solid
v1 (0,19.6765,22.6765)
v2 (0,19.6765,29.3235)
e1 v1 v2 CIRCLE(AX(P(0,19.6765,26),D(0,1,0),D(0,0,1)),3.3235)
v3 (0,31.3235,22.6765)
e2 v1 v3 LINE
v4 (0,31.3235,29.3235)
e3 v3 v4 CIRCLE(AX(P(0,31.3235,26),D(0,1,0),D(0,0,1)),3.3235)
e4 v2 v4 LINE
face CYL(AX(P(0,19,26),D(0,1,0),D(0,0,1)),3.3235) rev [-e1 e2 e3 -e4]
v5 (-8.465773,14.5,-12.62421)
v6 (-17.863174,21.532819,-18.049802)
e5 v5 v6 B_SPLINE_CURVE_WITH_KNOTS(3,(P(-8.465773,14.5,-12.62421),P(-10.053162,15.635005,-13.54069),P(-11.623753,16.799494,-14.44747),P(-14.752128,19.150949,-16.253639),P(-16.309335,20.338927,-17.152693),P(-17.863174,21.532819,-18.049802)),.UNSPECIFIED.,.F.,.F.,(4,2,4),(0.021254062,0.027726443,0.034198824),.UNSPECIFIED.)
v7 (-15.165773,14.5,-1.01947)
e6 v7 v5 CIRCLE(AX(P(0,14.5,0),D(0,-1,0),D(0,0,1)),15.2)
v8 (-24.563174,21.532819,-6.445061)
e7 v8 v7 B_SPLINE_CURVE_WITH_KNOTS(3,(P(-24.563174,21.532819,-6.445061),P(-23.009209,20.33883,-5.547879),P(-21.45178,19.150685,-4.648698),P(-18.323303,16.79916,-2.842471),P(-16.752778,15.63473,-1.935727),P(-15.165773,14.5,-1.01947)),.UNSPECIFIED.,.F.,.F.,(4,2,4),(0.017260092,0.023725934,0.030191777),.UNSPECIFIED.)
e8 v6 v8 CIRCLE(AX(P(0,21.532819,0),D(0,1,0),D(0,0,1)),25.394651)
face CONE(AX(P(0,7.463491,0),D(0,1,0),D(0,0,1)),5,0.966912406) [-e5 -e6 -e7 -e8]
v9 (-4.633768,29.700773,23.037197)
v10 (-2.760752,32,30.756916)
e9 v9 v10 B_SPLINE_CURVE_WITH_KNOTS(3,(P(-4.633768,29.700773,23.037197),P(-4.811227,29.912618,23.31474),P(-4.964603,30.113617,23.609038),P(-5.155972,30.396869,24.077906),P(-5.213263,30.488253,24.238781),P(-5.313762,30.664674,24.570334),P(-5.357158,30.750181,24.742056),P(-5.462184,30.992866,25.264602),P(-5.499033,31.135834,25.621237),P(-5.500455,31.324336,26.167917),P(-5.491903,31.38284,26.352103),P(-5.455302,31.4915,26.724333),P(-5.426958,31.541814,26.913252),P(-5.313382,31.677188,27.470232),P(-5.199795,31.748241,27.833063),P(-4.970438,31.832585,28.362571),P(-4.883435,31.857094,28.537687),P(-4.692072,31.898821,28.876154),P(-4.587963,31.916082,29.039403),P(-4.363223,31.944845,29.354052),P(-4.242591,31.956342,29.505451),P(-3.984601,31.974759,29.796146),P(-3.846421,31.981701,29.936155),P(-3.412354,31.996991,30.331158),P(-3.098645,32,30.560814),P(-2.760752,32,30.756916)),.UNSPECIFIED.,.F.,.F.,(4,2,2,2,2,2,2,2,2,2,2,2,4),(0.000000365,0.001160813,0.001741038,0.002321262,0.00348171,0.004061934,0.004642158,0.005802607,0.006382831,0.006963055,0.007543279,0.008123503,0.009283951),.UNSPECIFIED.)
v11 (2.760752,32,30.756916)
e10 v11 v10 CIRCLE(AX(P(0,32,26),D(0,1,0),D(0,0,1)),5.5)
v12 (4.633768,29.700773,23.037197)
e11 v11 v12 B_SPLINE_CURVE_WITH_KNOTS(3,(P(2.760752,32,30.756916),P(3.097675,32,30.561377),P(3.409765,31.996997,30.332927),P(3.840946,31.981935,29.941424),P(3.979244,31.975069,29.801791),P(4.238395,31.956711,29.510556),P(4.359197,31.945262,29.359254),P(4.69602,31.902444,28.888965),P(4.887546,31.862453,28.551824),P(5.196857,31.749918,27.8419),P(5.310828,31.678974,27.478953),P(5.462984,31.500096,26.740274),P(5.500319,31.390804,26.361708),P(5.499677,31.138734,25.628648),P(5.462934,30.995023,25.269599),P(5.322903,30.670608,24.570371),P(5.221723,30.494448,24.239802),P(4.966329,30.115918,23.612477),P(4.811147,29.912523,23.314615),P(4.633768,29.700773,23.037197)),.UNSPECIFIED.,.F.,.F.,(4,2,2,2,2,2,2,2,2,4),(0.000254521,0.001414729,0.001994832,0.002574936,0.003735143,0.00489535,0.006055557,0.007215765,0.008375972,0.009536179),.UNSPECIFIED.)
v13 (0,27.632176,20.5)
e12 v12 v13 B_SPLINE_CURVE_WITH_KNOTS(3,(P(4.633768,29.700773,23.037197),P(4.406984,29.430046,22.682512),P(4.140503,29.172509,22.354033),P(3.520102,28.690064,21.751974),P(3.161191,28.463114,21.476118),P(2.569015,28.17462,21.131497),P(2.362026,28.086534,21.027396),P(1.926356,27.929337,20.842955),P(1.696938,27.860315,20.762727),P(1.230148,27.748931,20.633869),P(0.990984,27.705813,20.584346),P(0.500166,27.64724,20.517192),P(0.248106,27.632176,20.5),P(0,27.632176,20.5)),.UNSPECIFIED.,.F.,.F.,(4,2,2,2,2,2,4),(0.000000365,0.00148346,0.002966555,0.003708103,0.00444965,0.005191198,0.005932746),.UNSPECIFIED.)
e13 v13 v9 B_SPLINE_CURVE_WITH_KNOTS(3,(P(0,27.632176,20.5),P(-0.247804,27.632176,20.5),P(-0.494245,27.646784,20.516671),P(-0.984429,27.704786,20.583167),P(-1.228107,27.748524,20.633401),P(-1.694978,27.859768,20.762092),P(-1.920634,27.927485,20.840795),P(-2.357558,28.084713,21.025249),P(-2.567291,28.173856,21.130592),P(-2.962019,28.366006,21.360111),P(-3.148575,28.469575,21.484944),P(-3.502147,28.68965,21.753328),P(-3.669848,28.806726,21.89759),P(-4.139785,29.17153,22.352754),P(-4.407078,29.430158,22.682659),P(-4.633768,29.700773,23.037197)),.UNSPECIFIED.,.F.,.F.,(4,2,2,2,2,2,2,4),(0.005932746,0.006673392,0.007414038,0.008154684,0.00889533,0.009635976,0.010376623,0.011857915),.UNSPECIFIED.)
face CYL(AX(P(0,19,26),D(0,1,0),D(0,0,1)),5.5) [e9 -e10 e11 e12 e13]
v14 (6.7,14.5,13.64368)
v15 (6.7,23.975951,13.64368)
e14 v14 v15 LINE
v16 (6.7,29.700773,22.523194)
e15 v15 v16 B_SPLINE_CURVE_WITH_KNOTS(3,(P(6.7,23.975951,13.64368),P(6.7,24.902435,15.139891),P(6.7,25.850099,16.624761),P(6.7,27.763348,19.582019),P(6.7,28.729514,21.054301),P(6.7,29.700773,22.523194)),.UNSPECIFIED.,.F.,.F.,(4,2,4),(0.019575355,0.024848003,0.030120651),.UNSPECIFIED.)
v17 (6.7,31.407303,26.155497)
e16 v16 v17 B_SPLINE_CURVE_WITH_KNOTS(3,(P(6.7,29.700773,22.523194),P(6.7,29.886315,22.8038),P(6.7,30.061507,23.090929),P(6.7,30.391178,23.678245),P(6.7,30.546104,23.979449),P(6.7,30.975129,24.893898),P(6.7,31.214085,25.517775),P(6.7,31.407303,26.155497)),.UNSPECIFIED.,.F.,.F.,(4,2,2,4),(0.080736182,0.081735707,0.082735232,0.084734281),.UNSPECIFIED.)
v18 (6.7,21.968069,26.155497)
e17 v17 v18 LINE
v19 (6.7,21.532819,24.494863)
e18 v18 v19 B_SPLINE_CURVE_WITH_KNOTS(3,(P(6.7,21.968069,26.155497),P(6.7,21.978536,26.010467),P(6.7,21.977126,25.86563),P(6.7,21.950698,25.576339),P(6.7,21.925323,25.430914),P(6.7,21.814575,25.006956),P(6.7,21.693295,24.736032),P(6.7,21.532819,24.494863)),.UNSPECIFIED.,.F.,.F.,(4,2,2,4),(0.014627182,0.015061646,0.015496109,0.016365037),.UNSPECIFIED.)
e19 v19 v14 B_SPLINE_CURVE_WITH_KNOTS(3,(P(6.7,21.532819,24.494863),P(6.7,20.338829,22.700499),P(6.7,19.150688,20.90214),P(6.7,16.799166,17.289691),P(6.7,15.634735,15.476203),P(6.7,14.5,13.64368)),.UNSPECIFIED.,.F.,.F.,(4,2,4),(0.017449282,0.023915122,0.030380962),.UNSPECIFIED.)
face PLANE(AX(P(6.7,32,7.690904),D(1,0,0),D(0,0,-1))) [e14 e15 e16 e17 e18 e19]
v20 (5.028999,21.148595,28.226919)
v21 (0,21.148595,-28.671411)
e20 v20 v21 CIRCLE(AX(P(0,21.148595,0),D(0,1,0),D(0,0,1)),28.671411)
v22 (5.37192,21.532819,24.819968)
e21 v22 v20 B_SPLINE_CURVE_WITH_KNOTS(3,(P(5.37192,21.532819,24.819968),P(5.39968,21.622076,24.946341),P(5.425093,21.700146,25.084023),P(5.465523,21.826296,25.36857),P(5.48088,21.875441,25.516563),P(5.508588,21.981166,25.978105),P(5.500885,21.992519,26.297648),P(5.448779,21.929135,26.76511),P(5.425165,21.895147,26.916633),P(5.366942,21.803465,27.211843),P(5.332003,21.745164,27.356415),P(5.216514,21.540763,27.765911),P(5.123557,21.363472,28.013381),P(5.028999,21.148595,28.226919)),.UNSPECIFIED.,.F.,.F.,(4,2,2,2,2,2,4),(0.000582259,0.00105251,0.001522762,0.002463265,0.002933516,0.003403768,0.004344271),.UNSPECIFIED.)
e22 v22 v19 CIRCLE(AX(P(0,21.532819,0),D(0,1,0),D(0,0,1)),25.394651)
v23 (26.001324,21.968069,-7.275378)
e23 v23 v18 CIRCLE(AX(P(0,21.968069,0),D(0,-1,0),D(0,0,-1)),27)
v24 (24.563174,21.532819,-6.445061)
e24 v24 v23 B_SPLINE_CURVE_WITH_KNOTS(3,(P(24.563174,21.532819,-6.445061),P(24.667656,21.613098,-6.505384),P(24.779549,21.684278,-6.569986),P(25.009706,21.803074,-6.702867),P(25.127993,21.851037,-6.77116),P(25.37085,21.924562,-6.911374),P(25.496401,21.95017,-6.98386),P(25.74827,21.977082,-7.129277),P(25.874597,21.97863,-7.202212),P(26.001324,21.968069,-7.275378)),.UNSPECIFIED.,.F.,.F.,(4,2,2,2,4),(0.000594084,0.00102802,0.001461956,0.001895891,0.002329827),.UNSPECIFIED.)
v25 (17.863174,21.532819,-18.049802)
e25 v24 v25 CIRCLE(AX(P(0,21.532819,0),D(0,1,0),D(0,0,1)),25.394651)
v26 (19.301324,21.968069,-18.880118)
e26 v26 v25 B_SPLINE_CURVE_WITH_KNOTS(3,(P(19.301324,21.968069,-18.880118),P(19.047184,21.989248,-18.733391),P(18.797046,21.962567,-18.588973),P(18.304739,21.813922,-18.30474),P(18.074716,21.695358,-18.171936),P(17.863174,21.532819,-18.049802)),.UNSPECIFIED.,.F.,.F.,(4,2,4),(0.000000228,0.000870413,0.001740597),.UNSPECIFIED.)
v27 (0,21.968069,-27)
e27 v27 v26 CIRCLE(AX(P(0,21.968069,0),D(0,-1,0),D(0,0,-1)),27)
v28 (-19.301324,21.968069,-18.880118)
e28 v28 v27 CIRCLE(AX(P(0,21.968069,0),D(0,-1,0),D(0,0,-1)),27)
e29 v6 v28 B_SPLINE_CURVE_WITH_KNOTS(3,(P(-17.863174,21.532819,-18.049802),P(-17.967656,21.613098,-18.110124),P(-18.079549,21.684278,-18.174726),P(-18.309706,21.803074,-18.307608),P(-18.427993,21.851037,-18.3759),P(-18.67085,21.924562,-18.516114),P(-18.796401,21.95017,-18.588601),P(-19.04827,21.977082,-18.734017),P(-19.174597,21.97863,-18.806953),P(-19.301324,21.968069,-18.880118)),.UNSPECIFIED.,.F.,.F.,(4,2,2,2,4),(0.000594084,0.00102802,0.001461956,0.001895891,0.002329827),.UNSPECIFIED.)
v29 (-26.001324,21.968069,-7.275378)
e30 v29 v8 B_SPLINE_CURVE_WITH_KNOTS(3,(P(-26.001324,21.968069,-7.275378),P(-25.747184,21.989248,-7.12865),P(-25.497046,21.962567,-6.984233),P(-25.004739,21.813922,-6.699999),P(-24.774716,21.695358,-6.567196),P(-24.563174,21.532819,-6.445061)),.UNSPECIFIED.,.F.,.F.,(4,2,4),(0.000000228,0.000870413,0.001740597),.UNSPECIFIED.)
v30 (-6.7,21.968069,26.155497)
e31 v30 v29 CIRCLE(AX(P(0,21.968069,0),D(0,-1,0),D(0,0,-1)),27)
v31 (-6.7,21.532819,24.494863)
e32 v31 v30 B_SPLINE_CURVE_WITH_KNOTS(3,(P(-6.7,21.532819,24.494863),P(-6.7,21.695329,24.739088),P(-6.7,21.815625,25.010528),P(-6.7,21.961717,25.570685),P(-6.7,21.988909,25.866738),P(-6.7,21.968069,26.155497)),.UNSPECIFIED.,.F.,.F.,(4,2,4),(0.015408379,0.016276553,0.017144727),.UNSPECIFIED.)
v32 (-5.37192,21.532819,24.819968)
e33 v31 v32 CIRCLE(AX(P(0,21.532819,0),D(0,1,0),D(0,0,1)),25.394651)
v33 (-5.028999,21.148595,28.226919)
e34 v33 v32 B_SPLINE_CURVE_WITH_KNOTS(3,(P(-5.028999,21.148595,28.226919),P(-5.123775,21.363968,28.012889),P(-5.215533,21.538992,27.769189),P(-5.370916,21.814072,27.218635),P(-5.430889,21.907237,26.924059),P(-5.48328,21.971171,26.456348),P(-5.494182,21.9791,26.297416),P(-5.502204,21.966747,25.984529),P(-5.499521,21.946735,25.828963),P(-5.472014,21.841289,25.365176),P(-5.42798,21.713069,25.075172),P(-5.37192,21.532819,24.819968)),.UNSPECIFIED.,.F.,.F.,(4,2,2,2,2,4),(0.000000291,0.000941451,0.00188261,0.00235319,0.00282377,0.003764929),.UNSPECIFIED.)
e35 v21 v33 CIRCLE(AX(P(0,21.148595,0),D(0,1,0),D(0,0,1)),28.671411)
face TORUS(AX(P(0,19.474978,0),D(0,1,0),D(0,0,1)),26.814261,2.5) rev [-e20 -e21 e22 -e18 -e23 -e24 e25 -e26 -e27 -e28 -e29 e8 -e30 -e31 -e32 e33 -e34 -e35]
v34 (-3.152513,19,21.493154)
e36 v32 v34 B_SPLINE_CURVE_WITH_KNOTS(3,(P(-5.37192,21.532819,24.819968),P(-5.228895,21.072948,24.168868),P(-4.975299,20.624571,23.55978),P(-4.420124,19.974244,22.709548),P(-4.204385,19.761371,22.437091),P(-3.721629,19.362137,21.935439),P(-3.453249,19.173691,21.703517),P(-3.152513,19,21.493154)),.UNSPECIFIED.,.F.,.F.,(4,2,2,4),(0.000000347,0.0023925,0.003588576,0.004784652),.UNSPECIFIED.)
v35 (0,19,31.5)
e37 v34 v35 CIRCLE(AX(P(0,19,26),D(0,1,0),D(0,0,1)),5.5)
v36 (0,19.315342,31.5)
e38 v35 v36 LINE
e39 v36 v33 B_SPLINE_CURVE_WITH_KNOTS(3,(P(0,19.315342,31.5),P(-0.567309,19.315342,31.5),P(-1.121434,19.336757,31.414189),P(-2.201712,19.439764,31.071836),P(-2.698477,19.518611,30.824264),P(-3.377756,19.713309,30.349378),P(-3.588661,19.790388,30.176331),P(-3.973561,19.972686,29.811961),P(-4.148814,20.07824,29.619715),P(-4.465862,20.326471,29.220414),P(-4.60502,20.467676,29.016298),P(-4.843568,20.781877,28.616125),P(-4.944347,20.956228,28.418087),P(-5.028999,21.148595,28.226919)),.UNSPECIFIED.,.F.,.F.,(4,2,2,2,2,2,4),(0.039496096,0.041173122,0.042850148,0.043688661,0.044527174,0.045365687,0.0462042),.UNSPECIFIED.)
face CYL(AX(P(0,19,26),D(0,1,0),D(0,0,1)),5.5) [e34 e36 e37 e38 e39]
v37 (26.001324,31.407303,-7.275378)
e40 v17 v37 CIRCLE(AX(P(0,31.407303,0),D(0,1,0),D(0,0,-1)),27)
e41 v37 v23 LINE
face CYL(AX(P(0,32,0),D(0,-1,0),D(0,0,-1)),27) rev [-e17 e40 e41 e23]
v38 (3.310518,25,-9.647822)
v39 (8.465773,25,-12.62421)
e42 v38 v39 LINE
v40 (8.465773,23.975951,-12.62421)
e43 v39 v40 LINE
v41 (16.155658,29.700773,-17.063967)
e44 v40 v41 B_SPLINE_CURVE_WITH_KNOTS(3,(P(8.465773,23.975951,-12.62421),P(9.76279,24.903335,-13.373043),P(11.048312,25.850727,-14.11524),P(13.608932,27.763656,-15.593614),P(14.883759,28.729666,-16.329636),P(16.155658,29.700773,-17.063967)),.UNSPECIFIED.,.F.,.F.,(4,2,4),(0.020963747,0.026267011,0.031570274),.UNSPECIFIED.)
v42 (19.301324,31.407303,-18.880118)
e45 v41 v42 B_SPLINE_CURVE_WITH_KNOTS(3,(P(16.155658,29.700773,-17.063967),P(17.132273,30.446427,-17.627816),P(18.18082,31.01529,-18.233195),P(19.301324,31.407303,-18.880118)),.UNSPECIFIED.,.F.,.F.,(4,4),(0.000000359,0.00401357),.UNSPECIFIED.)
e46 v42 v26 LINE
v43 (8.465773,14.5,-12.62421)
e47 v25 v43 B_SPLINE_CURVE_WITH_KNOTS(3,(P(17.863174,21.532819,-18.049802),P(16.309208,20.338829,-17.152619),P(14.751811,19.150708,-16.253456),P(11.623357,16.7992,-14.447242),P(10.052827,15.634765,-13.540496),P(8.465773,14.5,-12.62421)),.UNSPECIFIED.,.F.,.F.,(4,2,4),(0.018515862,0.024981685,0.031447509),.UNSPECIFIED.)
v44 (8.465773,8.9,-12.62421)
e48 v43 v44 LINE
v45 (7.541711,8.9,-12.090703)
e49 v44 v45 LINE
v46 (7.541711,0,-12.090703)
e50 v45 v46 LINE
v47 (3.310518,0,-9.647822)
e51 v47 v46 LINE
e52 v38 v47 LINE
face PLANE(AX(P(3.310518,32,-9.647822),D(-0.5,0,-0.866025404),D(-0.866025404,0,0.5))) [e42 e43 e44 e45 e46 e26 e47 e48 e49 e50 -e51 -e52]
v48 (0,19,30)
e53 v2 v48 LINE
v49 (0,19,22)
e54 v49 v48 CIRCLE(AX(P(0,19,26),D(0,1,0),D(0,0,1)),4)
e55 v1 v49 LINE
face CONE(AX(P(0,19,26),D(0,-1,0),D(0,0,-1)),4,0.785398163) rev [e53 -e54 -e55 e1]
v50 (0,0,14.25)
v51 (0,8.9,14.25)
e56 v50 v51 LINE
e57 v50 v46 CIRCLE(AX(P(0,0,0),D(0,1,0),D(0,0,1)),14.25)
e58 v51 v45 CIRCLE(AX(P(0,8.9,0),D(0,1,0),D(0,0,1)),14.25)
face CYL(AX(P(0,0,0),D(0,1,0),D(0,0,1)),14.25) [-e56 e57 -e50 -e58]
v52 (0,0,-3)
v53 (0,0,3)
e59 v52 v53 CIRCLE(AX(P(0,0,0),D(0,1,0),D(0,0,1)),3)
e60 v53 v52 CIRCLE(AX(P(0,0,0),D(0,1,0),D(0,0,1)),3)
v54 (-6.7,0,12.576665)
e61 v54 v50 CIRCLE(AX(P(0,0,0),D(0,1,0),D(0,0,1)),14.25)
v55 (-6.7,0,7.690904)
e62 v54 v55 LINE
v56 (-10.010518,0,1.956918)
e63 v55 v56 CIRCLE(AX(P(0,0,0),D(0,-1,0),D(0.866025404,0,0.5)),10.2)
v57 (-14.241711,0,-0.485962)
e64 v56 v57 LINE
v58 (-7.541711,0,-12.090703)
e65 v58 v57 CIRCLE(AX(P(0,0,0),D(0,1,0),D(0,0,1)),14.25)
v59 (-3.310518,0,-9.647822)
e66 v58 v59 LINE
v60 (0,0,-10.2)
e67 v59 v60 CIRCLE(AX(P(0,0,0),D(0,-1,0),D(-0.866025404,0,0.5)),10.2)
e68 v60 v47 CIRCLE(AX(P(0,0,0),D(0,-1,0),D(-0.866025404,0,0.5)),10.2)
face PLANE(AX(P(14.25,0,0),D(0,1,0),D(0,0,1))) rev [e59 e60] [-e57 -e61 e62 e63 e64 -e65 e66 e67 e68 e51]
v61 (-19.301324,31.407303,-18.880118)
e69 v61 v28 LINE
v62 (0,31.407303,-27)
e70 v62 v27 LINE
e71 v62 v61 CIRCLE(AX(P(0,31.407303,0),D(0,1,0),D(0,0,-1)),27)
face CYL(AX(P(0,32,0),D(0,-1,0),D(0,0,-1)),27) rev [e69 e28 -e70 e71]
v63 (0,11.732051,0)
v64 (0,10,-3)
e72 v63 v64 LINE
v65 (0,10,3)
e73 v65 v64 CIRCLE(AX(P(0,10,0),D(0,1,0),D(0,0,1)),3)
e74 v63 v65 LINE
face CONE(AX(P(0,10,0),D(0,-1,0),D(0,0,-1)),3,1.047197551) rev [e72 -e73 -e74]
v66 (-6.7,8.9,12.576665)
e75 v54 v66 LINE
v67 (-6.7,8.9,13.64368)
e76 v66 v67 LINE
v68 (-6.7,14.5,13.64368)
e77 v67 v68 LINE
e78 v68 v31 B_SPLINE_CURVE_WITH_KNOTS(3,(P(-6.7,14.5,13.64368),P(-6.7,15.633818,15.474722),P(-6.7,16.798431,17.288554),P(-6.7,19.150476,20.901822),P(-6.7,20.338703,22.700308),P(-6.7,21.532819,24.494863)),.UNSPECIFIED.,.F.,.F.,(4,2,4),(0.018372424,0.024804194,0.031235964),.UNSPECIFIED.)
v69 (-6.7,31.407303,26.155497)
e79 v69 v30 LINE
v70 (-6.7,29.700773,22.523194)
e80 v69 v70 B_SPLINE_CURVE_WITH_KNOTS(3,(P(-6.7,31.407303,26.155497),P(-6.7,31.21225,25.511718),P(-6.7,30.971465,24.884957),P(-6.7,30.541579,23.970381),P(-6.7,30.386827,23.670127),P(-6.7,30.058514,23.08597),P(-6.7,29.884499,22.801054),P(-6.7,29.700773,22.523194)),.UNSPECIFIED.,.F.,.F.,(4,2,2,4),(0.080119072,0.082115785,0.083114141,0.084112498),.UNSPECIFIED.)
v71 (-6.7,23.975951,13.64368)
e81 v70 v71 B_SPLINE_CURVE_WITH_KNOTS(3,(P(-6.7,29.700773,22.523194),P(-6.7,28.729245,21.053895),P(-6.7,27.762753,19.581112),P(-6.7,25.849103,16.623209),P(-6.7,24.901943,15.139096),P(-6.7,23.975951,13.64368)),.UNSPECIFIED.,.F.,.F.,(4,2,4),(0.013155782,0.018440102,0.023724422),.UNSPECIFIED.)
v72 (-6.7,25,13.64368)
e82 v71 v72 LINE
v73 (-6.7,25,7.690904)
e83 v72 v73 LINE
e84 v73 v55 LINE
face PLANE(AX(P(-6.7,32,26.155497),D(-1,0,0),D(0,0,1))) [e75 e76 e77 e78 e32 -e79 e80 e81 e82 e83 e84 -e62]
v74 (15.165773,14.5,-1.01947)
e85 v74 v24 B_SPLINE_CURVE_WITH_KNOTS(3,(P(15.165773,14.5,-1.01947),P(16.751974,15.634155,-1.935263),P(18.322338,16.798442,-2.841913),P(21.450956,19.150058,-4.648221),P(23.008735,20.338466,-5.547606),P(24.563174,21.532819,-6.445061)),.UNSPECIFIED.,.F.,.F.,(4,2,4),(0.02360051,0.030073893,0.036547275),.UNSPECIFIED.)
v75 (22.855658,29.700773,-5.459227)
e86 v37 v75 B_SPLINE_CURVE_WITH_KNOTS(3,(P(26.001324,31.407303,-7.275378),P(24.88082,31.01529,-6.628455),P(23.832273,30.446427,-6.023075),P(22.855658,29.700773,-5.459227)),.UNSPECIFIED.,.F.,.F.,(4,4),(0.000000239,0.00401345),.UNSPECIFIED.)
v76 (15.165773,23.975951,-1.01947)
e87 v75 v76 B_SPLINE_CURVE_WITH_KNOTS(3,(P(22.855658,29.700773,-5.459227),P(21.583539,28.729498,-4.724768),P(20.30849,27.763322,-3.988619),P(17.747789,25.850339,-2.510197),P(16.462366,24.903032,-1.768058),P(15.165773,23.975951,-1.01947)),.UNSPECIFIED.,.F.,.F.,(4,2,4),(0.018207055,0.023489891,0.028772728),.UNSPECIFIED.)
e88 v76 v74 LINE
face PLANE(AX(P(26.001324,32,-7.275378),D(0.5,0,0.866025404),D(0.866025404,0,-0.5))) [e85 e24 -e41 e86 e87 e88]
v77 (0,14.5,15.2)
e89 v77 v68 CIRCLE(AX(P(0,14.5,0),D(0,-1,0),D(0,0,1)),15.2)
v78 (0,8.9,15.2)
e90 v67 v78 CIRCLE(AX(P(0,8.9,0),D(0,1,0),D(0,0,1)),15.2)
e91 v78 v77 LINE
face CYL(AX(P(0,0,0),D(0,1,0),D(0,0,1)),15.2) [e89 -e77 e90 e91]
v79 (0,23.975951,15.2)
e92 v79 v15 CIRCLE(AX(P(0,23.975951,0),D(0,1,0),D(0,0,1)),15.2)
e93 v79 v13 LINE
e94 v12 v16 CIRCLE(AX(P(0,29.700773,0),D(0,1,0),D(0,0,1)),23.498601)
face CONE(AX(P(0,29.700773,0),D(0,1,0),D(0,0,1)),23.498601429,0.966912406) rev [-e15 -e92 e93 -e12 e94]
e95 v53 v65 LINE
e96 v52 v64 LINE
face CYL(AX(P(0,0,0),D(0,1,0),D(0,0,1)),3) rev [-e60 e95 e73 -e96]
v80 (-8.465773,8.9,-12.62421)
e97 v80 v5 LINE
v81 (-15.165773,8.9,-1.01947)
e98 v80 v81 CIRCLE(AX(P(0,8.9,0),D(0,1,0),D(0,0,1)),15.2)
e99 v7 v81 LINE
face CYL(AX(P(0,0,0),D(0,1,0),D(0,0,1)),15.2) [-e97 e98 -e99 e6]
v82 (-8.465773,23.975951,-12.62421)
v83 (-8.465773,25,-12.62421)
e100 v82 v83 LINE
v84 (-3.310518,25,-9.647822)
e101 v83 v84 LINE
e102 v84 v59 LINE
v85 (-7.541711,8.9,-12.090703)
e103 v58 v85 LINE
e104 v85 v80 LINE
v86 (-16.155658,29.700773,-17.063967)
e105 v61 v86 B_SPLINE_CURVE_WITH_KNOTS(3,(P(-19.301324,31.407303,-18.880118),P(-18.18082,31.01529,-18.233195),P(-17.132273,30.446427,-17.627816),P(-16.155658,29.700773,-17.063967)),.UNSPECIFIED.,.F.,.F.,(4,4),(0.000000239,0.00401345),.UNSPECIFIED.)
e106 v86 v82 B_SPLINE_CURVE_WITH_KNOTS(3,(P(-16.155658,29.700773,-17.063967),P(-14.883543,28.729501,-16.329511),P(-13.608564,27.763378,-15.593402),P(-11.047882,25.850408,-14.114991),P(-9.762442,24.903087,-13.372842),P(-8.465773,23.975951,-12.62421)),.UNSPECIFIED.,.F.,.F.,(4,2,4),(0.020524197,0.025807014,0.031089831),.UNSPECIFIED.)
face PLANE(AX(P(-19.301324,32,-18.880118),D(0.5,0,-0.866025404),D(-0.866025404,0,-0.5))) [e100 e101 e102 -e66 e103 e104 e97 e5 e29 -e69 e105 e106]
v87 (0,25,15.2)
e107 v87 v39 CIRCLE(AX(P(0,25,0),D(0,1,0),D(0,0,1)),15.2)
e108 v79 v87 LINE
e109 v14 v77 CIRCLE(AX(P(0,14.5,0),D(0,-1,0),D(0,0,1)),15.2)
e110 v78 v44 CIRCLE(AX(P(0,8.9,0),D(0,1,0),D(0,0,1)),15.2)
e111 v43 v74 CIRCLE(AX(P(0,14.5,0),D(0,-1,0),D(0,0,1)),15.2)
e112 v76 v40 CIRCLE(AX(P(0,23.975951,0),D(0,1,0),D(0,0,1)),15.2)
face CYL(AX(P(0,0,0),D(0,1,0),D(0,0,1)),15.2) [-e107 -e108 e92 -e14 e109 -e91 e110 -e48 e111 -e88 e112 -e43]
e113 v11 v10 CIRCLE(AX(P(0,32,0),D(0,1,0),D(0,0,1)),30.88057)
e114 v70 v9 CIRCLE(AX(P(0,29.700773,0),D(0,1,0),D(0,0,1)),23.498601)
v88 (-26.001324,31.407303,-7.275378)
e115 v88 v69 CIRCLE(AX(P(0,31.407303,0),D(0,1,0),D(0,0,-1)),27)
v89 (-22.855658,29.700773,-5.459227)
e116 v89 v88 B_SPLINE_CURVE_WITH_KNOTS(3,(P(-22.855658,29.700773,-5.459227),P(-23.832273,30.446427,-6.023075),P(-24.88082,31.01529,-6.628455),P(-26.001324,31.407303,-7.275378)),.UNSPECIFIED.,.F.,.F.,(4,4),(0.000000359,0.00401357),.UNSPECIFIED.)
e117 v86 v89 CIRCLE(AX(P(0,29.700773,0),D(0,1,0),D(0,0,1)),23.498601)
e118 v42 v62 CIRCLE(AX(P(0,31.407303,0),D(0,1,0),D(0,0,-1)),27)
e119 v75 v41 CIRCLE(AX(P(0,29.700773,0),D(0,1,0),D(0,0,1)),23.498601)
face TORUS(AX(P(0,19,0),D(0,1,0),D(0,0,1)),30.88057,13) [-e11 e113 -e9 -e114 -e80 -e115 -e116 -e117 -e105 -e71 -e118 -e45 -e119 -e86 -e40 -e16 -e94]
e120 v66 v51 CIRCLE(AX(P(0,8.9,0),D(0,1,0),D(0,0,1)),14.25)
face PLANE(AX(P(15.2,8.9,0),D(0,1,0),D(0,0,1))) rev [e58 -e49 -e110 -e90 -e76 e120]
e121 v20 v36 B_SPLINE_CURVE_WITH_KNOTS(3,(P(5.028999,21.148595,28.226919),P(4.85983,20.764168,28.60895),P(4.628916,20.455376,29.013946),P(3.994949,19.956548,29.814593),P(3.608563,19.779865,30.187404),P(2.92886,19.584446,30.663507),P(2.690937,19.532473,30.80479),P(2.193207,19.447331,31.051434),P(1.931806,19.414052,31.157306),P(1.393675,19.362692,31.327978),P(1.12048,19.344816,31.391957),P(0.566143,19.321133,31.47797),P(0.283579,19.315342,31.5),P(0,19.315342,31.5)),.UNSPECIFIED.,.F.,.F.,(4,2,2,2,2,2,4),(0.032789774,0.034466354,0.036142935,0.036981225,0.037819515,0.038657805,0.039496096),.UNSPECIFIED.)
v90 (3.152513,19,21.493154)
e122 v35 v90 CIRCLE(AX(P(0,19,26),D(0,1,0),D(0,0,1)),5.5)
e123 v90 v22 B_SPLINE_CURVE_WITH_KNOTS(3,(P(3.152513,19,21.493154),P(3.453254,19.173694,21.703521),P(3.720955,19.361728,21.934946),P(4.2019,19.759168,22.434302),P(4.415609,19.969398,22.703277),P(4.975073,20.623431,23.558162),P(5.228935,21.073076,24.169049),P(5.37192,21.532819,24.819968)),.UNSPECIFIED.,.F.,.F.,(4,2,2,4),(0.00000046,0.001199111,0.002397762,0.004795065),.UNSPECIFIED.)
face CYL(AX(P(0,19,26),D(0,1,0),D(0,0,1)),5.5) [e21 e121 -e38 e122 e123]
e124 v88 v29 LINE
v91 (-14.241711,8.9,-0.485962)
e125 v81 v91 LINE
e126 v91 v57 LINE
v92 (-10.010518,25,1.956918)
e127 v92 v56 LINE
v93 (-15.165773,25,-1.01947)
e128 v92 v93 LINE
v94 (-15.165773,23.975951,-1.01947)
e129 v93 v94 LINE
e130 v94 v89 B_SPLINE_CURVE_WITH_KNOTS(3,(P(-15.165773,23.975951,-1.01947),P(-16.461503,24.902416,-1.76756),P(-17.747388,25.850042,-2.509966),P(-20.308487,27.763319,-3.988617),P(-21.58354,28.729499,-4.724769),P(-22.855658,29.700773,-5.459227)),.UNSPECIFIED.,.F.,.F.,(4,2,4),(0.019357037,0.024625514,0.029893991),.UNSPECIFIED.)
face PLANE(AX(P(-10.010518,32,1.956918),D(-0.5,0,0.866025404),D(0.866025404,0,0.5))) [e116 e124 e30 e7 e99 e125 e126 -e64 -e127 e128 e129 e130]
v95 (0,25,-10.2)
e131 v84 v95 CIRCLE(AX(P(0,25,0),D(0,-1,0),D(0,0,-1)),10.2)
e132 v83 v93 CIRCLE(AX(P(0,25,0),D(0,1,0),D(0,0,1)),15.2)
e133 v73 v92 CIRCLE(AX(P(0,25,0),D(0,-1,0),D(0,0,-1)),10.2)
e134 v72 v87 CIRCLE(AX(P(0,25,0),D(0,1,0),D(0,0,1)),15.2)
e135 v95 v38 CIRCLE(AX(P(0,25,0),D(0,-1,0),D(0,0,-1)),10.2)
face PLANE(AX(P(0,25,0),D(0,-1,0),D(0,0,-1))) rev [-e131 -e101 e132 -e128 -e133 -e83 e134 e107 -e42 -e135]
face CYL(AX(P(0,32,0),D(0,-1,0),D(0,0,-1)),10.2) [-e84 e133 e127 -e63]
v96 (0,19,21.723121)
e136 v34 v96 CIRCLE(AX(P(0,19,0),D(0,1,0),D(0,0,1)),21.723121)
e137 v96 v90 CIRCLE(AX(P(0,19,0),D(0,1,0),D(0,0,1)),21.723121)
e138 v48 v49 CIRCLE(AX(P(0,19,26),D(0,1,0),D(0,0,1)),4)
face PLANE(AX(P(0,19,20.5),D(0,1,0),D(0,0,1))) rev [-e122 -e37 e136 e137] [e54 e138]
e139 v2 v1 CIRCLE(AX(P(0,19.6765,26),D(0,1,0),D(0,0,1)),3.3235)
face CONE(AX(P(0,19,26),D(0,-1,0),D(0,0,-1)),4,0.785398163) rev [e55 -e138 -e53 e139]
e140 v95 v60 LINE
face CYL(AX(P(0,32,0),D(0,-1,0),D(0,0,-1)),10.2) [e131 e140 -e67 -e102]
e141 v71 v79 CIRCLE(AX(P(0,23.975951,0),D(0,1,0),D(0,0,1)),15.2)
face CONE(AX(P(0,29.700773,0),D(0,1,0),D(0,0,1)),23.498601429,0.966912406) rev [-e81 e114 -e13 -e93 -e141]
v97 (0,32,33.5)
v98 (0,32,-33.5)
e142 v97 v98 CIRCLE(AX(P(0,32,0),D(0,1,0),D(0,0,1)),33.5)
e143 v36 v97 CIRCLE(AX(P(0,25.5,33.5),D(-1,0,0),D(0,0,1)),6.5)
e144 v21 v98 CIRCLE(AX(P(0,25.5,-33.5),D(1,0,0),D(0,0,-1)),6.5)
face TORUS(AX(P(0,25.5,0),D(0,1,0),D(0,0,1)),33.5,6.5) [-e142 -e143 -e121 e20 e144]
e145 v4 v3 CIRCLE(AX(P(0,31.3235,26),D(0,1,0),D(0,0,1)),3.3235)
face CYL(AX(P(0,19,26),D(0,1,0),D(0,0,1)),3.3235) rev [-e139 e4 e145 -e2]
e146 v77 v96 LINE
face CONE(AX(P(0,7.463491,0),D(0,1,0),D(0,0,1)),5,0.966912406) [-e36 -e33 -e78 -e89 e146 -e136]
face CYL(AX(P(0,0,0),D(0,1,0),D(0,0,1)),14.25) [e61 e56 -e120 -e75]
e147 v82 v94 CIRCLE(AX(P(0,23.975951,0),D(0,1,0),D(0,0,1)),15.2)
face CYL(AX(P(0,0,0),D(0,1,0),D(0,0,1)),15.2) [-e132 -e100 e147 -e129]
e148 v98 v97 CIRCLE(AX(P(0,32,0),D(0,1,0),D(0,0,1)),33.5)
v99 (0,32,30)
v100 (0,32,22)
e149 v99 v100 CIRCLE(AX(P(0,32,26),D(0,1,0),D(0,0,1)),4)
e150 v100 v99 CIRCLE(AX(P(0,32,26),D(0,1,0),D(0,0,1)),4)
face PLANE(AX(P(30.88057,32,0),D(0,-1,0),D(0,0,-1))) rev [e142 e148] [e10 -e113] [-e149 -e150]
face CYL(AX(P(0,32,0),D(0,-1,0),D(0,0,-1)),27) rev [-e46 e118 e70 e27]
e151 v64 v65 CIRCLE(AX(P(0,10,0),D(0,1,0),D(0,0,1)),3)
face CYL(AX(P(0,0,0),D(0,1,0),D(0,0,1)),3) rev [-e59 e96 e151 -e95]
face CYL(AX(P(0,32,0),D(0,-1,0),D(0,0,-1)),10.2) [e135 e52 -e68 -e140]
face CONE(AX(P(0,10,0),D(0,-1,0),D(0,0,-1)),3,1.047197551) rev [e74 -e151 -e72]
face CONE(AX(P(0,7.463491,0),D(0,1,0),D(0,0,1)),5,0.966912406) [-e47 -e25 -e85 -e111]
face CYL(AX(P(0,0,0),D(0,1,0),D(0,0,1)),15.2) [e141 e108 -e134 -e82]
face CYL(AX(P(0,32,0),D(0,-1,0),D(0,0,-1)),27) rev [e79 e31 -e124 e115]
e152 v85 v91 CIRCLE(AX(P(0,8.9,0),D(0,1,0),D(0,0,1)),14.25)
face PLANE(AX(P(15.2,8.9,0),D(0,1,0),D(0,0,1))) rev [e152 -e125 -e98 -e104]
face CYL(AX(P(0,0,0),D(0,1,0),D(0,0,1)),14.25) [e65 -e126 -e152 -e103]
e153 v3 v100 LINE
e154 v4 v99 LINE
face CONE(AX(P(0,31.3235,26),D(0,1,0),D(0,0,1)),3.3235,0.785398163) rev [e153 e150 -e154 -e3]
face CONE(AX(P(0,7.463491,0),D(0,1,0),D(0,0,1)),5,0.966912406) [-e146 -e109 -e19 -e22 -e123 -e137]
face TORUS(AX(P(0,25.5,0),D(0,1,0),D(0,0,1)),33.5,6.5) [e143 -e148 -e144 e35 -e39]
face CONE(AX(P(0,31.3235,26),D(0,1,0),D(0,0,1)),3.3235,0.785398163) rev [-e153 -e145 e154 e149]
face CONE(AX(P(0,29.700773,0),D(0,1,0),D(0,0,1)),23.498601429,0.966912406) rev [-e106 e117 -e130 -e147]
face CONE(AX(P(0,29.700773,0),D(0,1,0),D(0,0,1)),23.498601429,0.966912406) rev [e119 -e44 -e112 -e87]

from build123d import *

# Parameters (mm, degrees)
CUT_EXTRUDE1_DEPTH = 32
SKETCH5_W          = 5.5
SKETCH5_H          = 13
CIRPATTERN1_COUNT  = 3


with BuildPart() as part:
    # Sketch1 → Revolve1 (revolve)
    with BuildSketch(Plane.XY, mode=Mode.PRIVATE) as revolve1_sk:
        with BuildLine():
            Line((0, 20), (5, 20))
            Line((5, 20), (5, 16.939442451))
            Line((5, 16.939442451), (23.498601429, 29.700772791))
            ThreePointArc((23.498601429, 29.700772791), (27.014696752, 31.411890394), (30.880570115, 32))
            Line((30.880570115, 32), (33.5, 32))
            ThreePointArc((33.5, 32), (39.438608051, 22.857475748), (28.671410524, 21.148595207))
            ThreePointArc((28.671410524, 21.148595207), (27.10540909, 21.957966627), (25.394651363, 21.5328189))
            Line((25.394651363, 21.5328189), (5, 7.463491323))
            Line((5, 7.463491323), (5, 2))
            Line((5, 2), (0, 2))
            Line((0, 2), (0, 20))
        make_face()
    revolve(revolve1_sk.sketch.rotate(Axis((0, 0, 0), (0, 1, 0)), 270), axis=Axis((0, 0, 0), (0, 1, 0)))

    # Sketch2 → Cut-Extrude1 (cut)
    with BuildSketch(Plane(origin=(0, 0, 0), x_dir=(1, 0, 0), z_dir=(0, 1, 0))):
        with BuildLine():
            Line((26.001324465, 7.275378072), (10.010517998, -1.956918346))
            ThreePointArc((10.010517998, -1.956918346), (8.833459119, -5.1), (6.7, -7.690903718))
            Line((6.7, -7.690903718), (6.7, -26.155496554))
            ThreePointArc((6.7, -26.155496554), (23.382685902, -13.5), (26.001324465, 7.275378072))
        make_face()
    cut_extrude1 = extrude(amount=CUT_EXTRUDE1_DEPTH, mode=Mode.SUBTRACT)

    # Sketch4 → Revolve2 (revolve)
    with BuildSketch(Plane.XY, mode=Mode.PRIVATE) as revolve2_sk:
        Polygon((0, 25), (15.2, 25), (15.2, 8.9), (14.25, 8.9), (14.25, 0), (0, 0), align=None)
    revolve(revolve2_sk.sketch.rotate(Axis((0, 0, 0), (0, 1, 0)), 270), axis=Axis((0, 0, 0), (0, 1, 0)))

    # Sketch5 → Revolve3 (revolve)
    with BuildSketch(Plane(origin=(0, 0, 0), x_dir=(0, 0, -1), z_dir=(1, 0, 0))):
        with Locations((-23.25, 25.5)):
            Rectangle(SKETCH5_W, SKETCH5_H)
    revolve(axis=Axis((0, 19, 26), (0, 1, 0)))

    # Sketch6 → Cut-Revolve1 (revolve, cut)
    with BuildSketch(Plane(origin=(0, 0, 0), x_dir=(0, 0, -1), z_dir=(1, 0, 0)), mode=Mode.PRIVATE) as cut_revolve1_sk:
        Polygon((-26, 32), (-22, 32), (-22.6765, 31.3235), (-22.6765, 19.6765), (-22, 19), (-26, 19), align=None)
    revolve(cut_revolve1_sk.sketch.rotate(Axis((0, 19, 26), (0, 1, 0)), 180), axis=Axis((0, 19, 26), (0, 1, 0)), mode=Mode.SUBTRACT)

    # Sketch7 → Cut-Revolve2 (revolve, cut)
    with BuildSketch(Plane.XY, mode=Mode.PRIVATE) as cut_revolve2_sk:
        Polygon((0, 11.732050808), (3, 10), (3, 0), (0, 0), align=None)
    revolve(cut_revolve2_sk.sketch.rotate(Axis((0, 0, 0), (0, 1, 0)), 270), axis=Axis((0, 0, 0), (0, 1, 0)), mode=Mode.SUBTRACT)

    # CirPattern1: Cut-Extrude1 ×3 about axis
    cirpattern1_axis = Axis((0, 0, 0), (0, 1, 0))
    for i in range(1, CIRPATTERN1_COUNT):
        add(cut_extrude1.rotate(cirpattern1_axis, i * 360 / CIRPATTERN1_COUNT), mode=Mode.SUBTRACT)


solid = part.part
